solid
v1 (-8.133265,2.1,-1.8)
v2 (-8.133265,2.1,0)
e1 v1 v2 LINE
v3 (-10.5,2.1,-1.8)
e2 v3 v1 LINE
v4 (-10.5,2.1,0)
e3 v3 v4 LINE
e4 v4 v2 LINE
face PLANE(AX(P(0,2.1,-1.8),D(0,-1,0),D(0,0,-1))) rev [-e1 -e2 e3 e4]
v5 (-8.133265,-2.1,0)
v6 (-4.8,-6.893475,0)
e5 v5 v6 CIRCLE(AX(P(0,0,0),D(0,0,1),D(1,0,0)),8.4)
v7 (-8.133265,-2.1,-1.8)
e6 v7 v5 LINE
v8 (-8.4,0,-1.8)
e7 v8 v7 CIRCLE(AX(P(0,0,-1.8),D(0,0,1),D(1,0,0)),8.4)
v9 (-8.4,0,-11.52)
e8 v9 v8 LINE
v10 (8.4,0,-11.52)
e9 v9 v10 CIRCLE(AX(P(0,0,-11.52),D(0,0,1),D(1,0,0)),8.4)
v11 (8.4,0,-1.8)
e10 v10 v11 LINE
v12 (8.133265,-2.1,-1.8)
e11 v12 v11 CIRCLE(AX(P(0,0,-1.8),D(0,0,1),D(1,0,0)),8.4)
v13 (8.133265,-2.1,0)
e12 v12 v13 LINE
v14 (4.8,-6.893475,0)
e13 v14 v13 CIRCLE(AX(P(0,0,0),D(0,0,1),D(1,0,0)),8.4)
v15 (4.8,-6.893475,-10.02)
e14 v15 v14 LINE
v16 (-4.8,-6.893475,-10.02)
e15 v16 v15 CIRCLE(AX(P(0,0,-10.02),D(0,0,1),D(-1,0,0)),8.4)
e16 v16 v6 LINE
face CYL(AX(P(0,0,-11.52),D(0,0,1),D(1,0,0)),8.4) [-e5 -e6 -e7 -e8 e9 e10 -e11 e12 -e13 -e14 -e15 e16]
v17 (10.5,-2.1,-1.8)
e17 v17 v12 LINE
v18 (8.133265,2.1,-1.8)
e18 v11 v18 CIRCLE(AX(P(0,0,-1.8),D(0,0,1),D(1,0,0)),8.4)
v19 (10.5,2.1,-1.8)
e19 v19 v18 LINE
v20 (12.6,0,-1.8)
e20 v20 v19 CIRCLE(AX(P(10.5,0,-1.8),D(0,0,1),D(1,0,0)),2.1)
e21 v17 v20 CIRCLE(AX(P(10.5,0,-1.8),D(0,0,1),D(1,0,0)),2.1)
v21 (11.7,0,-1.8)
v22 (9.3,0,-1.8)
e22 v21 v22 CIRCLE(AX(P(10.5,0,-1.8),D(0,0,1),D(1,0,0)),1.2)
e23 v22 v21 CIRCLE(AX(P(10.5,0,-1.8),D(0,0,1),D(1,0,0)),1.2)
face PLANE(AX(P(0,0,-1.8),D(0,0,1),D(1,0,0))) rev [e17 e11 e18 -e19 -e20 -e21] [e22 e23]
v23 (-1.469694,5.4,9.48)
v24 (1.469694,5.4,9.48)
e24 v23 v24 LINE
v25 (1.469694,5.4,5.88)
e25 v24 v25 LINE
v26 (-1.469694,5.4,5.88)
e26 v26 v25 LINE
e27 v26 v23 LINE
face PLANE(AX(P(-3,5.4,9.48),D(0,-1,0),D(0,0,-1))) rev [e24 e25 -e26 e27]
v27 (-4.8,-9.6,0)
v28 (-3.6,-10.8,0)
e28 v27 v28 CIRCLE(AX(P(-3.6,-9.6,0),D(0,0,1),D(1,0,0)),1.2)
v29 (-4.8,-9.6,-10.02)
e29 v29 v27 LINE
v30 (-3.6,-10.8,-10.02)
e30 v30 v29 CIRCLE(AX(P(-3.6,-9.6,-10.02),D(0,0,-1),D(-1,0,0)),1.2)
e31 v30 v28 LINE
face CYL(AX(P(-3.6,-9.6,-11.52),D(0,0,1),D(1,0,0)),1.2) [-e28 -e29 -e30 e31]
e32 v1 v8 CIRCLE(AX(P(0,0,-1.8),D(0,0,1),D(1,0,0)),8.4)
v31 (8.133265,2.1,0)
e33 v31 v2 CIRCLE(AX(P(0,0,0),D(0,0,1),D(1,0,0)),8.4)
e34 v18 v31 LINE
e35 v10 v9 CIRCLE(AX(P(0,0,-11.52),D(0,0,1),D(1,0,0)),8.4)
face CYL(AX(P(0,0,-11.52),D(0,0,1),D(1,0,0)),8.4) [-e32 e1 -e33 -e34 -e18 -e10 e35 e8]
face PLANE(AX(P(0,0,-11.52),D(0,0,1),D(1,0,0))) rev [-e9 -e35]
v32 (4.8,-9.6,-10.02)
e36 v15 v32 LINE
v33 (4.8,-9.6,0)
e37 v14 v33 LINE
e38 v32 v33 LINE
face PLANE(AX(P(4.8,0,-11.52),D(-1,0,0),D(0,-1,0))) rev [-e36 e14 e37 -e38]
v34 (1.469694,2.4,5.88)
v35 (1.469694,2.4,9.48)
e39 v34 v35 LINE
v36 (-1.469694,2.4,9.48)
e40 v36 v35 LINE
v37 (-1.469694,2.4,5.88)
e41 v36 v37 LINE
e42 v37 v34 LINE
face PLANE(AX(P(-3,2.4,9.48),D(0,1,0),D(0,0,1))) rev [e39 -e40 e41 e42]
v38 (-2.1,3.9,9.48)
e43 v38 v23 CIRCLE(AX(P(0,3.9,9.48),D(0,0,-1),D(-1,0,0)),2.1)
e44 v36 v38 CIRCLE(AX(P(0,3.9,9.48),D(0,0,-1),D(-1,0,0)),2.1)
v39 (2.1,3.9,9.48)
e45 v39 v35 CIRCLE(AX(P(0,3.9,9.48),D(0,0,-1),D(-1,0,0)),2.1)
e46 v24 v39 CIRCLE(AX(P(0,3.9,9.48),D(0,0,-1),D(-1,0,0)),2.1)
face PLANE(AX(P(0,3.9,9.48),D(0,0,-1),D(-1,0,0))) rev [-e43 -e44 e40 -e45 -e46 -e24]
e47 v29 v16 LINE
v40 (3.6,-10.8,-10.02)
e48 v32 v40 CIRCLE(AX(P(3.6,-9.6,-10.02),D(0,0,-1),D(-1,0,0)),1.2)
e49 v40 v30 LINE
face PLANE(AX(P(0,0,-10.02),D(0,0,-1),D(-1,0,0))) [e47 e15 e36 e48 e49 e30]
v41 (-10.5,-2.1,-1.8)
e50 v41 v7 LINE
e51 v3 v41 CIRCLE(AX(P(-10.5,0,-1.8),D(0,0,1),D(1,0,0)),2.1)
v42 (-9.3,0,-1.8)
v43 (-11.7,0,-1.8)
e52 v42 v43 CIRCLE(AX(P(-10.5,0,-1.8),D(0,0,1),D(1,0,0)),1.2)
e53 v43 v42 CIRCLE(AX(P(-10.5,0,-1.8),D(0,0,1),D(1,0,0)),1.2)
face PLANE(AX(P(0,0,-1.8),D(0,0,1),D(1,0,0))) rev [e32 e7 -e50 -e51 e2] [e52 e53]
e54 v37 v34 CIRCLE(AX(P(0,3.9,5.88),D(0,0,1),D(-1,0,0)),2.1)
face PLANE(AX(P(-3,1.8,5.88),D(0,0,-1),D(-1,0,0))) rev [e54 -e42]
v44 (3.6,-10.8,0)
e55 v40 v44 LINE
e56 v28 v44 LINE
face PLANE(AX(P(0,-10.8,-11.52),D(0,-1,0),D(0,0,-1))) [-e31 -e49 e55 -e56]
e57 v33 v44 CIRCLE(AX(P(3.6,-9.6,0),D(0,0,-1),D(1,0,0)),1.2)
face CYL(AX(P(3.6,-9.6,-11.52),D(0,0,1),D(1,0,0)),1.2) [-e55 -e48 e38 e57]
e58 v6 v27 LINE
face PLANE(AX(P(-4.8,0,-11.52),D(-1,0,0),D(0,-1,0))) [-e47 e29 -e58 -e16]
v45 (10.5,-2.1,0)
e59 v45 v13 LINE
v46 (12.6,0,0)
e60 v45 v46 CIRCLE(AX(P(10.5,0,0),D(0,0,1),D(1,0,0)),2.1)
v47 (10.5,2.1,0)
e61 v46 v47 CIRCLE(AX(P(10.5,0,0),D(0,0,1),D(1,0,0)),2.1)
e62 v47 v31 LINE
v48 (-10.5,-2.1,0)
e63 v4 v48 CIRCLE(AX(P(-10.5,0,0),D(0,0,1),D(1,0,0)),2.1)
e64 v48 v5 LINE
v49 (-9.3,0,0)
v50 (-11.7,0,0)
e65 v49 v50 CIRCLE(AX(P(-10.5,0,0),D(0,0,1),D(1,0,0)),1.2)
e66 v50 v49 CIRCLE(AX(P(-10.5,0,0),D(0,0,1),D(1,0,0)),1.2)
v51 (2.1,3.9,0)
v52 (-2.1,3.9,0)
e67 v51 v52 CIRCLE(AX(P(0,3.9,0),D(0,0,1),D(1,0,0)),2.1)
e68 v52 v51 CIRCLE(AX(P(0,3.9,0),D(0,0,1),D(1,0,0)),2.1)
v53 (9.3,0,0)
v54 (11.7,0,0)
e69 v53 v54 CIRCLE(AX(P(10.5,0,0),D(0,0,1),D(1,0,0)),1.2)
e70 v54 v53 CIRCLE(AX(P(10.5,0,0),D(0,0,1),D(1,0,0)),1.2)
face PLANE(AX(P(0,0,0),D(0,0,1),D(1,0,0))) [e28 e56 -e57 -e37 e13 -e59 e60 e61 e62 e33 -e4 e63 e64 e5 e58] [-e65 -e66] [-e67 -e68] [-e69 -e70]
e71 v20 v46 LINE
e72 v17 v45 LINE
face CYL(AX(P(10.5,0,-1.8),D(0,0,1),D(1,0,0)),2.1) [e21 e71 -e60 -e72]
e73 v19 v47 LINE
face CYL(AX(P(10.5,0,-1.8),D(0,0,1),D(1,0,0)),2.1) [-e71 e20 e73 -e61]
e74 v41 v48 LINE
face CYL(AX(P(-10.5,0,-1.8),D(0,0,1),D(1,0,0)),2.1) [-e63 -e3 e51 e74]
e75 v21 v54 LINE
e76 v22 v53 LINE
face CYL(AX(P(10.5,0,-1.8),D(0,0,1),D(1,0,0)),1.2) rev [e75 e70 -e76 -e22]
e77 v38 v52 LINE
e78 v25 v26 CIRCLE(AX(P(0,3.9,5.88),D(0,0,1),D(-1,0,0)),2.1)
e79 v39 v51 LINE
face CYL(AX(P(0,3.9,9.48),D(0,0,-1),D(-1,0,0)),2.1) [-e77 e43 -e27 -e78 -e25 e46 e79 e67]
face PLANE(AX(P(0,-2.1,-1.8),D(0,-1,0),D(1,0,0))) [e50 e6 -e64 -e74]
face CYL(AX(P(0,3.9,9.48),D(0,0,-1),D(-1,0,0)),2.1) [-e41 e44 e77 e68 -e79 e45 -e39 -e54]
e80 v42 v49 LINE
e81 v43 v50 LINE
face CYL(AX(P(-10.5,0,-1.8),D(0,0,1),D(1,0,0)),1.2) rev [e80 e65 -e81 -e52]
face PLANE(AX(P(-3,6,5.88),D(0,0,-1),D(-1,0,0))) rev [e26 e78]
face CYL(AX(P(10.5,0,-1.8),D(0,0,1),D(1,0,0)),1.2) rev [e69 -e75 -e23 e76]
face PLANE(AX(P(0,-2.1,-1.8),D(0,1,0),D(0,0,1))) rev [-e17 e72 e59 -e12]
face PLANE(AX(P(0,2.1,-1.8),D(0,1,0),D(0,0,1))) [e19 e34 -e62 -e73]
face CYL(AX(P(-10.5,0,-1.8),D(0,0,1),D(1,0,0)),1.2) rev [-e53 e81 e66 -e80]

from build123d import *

# Parameters (mm, degrees)
SKETCH_1_3_R        = 2.5
BOSS_EXTRUDE1_DEPTH = 19.2
SKETCH_1_3_2_R      = 2
BOSS_EXTRUDE2_DEPTH = 3
SKETCH2_R           = 3.5
BOSS_EXTRUDE3_DEPTH = 35
CUT_EXTRUDE1_START  = -2.5
CUT_EXTRUDE1_DEPTH  = 2.5
SKETCH6_W           = 6
SKETCH6_H           = 1
CUT_EXTRUDE2_DEPTH  = 5
SCALE1_SCALE        = 0.6


with BuildPart() as part:
    # Sketch 1_3 → Boss-Extrude1 (new body)
    # profile 1 of 3: a face of its own
    with BuildSketch(Plane.XY):
        with BuildLine():
            ThreePointArc((14, 0), (0, 14), (-14, 0))
            ThreePointArc((-14, 0), (0, -14), (14, 0))
        make_face()
        with Locations((0, 6.5)):
            Circle(SKETCH_1_3_R, mode=Mode.SUBTRACT)
    # profile 2 of 3: a face of its own
    with BuildSketch(Plane.XY):
        with BuildLine():
            Line((8, -16), (8, -11.489125293))
            ThreePointArc((8, -11.489125293), (4.192388692, -13.357540082), (0, -14))
            Line((0, -14), (0, -18))
            Line((0, -18), (6, -18))
            ThreePointArc((6, -18), (7.414213562, -17.414213562), (8, -16))
        make_face()
    # profile 3 of 3: a face of its own
    with BuildSketch(Plane.XY):
        with BuildLine():
            Line((0, -18), (0, -14))
            ThreePointArc((0, -14), (-4.192388692, -13.357540082), (-8, -11.489125293))
            Line((-8, -11.489125293), (-8, -16))
            ThreePointArc((-8, -16), (-7.414213562, -17.414213562), (-6, -18))
            Line((-6, -18), (0, -18))
        make_face()
    extrude(amount=-BOSS_EXTRUDE1_DEPTH)

    # Sketch 1_3 2 → Boss-Extrude2 (add)
    # profile 1 of 2: a face of its own
    with BuildSketch(Plane.XY):
        with BuildLine():
            ThreePointArc((-14, 0), (-13.888415748, 1.764060095), (-13.555441712, 3.5))
            Line((-13.555441712, 3.5), (-17.5, 3.5))
            ThreePointArc((-17.5, 3.5), (-21, 0), (-17.5, -3.5))
            Line((-17.5, -3.5), (-13.555441712, -3.5))
            ThreePointArc((-13.555441712, -3.5), (-13.888415748, -1.764060095), (-14, 0))
        make_face()
        with Locations((-17.5, 0)):
            Circle(SKETCH_1_3_2_R, mode=Mode.SUBTRACT)
    # profile 2 of 2: a face of its own
    with BuildSketch(Plane.XY):
        with BuildLine():
            Line((13.555441712, -3.5), (17.5, -3.5))
            ThreePointArc((17.5, -3.5), (21, 0), (17.5, 3.5))
            Line((17.5, 3.5), (13.555441712, 3.5))
            ThreePointArc((13.555441712, 3.5), (13.888415748, 1.764060095), (14, 0))
            ThreePointArc((14, 0), (13.888415748, -1.764060095), (13.555441712, -3.5))
        make_face()
        with Locations((17.5, 0)):
            Circle(SKETCH_1_3_2_R, mode=Mode.SUBTRACT)
    extrude(amount=-BOSS_EXTRUDE2_DEPTH)

    # Sketch2 → Boss-Extrude3 (add)
    with BuildSketch(Plane(origin=(0, 0, -19.2), x_dir=(-1, 0, 0), z_dir=(0, 0, -1))):
        with Locations((0, 6.5)):
            Circle(SKETCH2_R)
    extrude(amount=-BOSS_EXTRUDE3_DEPTH)

    # Sketch5 → Cut-Extrude1 (cut)
    with BuildSketch(Plane(origin=(0, 0, -19.2), x_dir=(-1, 0, 0), z_dir=(0, 0, -1)).offset(CUT_EXTRUDE1_START)):
        with BuildLine():
            Line((-8, -11.489125293), (-8, -16))
            ThreePointArc((-8, -16), (-7.414213562, -17.414213562), (-6, -18))
            Line((-6, -18), (6, -18))
            ThreePointArc((6, -18), (7.414213562, -17.414213562), (8, -16))
            Line((8, -16), (8, -11.489125293))
            ThreePointArc((8, -11.489125293), (0, -14), (-8, -11.489125293))
        make_face()
    extrude(amount=CUT_EXTRUDE1_DEPTH, mode=Mode.SUBTRACT)

    # Sketch6 → Cut-Extrude2 (cut, symmetric)
    with BuildSketch(Plane(origin=(0, 0, 0), x_dir=(0, 0, -1), z_dir=(1, 0, 0))):
        with Locations((-12.8, 9.5)):
            Rectangle(SKETCH6_W, SKETCH6_H)
        with Locations((-12.8, 3.5)):
            Rectangle(SKETCH6_W, SKETCH6_H)
    extrude(amount=CUT_EXTRUDE2_DEPTH, both=True, mode=Mode.SUBTRACT)


with BuildPart() as part_1:
    # Scale1: scaled about (0, 0, 0)
    add(part.part.scale(SCALE1_SCALE))


solid = part_1.part
